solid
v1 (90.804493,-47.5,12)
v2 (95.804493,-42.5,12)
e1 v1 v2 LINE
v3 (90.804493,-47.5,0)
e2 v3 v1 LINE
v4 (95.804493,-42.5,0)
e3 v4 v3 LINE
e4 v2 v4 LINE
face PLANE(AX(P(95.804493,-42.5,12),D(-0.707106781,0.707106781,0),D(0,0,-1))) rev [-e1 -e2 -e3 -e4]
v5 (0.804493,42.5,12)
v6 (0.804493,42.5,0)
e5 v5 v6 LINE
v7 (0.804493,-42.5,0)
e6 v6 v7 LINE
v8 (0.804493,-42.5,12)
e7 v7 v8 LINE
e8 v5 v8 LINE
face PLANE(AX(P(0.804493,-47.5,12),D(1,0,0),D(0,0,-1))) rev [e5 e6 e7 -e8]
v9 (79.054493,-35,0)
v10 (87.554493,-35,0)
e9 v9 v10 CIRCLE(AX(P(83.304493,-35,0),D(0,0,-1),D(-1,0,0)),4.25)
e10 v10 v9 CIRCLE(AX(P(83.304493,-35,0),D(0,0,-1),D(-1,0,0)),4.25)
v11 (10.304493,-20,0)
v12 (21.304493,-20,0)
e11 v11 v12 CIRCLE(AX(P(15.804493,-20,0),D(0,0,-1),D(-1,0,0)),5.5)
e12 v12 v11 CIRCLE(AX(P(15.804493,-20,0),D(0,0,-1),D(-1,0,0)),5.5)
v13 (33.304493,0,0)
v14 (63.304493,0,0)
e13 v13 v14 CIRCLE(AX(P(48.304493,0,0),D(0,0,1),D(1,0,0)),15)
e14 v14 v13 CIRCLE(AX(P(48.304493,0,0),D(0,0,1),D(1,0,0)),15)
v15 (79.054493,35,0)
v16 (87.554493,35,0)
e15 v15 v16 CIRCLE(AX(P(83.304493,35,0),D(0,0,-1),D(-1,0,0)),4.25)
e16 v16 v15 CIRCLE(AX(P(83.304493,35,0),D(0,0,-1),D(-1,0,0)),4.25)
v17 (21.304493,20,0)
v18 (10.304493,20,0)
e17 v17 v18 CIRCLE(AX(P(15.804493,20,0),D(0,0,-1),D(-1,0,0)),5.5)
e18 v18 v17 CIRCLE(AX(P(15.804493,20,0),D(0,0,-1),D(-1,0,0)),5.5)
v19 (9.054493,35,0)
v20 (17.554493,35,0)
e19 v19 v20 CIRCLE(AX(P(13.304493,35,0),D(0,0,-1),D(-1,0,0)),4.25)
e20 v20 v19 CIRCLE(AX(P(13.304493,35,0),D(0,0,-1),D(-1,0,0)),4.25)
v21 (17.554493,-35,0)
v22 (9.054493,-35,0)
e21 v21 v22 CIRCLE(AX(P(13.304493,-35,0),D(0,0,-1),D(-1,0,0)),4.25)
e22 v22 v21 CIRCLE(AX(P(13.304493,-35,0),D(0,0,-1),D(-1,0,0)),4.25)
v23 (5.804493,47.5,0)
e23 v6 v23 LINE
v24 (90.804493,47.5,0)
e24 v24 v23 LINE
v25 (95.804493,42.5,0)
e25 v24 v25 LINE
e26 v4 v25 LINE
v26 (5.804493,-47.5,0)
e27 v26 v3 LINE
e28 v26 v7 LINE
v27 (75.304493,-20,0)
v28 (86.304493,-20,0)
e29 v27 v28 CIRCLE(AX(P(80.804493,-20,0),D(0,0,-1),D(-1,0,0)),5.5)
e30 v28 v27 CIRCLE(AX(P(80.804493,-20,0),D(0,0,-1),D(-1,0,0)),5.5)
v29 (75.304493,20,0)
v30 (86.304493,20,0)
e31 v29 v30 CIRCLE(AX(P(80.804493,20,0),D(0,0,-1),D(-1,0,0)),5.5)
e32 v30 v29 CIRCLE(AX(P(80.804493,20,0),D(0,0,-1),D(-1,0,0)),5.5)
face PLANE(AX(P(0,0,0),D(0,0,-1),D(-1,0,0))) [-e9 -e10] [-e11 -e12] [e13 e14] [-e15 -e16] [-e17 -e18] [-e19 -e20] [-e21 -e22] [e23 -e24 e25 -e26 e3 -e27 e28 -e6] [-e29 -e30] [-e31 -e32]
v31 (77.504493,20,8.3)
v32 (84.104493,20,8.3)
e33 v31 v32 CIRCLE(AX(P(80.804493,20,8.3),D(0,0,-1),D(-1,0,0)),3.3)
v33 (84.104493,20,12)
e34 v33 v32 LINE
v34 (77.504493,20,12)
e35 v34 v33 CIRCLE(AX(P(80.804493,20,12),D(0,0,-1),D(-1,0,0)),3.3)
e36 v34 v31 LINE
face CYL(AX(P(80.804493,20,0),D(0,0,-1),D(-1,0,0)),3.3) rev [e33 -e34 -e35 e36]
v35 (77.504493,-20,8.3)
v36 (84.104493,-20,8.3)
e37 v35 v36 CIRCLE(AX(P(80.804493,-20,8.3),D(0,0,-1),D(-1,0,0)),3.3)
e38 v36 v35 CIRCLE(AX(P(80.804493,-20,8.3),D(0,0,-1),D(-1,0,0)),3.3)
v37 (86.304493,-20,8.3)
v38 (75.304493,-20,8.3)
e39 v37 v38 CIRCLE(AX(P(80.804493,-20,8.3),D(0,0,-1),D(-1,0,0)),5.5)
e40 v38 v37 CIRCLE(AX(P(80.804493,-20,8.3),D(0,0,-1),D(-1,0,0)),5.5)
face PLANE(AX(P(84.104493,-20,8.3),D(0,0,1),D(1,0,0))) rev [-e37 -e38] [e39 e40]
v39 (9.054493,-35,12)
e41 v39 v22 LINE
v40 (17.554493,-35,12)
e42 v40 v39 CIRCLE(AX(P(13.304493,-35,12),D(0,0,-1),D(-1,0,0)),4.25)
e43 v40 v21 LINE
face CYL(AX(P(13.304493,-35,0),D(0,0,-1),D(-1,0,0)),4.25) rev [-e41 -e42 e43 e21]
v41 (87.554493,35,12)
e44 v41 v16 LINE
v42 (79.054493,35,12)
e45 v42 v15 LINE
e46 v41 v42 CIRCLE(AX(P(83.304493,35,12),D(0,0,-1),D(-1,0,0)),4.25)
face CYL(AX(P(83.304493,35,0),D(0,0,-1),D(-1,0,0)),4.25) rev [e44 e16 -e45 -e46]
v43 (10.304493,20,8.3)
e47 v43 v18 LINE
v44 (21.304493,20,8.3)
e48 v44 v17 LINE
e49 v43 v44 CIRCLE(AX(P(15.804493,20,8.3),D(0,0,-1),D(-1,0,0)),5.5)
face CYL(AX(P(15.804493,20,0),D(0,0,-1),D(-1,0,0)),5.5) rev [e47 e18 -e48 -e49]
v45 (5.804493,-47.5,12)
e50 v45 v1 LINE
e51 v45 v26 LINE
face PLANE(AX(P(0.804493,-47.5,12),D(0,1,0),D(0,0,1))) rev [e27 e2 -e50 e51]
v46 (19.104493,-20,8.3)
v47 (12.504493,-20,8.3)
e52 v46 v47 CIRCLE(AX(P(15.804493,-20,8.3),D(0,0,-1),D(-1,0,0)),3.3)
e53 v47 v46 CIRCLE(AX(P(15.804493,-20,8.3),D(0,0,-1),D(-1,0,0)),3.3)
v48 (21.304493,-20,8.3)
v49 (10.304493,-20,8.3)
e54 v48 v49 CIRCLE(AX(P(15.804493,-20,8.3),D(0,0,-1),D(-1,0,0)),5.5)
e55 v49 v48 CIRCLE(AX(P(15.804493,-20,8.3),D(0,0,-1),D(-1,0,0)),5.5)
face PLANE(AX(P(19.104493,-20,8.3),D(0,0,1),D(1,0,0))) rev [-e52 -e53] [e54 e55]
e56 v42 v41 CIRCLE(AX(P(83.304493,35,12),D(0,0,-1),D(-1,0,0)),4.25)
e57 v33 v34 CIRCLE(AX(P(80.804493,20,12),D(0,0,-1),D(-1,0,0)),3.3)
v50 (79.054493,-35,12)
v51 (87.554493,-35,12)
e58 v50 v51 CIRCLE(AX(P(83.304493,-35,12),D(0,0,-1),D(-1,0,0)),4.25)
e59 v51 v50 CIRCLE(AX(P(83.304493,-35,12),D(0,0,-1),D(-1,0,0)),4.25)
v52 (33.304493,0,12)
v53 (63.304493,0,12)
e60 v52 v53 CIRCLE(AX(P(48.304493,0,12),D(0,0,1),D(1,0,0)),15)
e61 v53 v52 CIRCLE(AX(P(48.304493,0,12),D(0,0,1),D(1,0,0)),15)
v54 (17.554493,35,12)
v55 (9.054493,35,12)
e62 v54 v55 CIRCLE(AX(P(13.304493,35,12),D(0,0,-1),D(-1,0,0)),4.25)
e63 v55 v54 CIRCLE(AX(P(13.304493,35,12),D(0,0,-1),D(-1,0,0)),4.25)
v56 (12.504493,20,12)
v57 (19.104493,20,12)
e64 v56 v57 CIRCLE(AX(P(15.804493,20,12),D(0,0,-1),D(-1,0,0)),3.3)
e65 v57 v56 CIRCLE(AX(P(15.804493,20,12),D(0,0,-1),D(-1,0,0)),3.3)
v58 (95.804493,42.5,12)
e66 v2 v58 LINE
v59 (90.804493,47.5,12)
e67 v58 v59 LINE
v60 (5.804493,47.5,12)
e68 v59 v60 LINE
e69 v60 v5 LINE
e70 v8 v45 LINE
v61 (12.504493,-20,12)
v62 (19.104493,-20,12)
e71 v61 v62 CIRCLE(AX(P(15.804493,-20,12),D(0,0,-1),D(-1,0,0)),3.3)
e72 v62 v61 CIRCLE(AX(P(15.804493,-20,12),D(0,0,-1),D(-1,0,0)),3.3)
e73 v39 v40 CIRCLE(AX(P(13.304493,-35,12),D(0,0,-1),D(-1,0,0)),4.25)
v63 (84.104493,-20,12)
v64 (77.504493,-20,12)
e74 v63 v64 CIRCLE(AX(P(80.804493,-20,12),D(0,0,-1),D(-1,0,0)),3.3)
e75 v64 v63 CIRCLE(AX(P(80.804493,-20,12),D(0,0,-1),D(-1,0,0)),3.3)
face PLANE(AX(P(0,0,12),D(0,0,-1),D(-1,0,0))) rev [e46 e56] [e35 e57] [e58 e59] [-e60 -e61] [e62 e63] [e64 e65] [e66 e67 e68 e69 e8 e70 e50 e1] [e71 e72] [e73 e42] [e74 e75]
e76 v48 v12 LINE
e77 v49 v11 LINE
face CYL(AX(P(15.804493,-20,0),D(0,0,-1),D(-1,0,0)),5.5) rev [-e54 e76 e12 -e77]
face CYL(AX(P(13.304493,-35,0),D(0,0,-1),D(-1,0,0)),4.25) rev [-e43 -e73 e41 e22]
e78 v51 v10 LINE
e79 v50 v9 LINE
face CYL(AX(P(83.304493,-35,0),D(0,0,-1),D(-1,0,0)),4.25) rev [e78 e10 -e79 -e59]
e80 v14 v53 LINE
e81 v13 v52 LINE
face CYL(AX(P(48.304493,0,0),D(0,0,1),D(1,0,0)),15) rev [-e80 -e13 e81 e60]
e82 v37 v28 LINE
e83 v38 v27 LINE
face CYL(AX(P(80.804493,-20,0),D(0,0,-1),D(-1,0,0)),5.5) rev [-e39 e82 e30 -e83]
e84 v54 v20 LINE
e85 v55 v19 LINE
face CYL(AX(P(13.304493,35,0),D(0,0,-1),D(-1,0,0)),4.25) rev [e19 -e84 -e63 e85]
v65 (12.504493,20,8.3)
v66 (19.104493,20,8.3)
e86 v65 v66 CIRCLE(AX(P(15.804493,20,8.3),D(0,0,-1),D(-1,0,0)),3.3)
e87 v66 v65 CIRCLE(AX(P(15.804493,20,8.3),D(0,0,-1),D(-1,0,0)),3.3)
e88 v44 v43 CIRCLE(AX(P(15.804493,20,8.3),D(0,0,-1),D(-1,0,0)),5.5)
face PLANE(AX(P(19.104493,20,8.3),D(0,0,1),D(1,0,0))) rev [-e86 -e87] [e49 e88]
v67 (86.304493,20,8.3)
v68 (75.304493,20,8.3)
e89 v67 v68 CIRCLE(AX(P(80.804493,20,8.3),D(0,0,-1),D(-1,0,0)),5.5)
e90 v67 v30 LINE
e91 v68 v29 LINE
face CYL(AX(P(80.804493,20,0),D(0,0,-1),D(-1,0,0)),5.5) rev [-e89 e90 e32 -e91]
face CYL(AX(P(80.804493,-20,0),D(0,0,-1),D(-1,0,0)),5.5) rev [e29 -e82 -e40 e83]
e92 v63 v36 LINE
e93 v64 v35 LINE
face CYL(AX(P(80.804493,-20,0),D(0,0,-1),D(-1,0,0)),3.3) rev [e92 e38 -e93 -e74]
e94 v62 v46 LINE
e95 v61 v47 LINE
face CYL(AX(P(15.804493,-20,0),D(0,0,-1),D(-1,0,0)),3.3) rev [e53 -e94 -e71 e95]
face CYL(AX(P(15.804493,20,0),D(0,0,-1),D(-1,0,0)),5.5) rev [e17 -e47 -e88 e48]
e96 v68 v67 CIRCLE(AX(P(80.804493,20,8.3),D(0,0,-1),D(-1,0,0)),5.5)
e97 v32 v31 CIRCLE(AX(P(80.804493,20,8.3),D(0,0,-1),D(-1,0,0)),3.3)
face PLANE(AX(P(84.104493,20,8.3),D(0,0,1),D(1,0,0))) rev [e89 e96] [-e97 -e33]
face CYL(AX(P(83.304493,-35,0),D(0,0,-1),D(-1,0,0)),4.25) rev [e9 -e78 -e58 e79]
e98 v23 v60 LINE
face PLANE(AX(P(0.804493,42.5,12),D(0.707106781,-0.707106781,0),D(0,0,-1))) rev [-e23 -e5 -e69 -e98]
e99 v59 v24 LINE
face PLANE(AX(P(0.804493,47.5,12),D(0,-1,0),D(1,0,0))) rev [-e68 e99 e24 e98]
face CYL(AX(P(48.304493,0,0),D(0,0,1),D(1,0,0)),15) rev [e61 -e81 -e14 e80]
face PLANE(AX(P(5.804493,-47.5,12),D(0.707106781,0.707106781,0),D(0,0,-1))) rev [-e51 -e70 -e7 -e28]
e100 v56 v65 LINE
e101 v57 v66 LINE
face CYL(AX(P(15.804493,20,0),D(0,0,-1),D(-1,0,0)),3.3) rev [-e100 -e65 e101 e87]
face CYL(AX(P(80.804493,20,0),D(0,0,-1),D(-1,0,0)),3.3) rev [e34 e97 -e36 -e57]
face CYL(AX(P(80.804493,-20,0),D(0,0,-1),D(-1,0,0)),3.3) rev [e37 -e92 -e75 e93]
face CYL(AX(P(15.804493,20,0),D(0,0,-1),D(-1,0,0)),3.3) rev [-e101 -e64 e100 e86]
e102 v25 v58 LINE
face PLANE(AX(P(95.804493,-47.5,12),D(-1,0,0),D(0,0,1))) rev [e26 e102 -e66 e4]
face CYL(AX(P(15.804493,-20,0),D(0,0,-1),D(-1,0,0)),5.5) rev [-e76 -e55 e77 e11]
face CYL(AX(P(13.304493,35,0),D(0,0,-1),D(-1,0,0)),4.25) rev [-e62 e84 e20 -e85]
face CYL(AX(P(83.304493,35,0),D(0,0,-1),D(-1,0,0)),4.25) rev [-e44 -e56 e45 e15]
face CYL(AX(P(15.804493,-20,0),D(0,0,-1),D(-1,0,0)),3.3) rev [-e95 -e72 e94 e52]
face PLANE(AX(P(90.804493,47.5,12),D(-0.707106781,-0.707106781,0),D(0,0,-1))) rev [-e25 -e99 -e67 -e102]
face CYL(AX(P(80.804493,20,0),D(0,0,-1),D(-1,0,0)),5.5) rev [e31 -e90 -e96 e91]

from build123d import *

# Parameters (mm, degrees)
SKETCH_1_W                = 95
SKETCH_1_H                = 95
EXTRUDE_1_DEPTH           = 12
SKETCH_2_R                = 15
CUT_EXTRUDE_1_DEPTH       = 108.604604424
HOLE_WIZARD_1_D           = 6.6
HOLE_WIZARD_1_CBORE_D     = 11
HOLE_WIZARD_1_CBORE_DEPTH = 8.3
HOLE_WIZARD_M10_2_D       = 8.5
CHAMFER_1_SIZE            = 5


with BuildPart() as part:
    # 草图1 → 凸台-拉伸1 (new body)
    with BuildSketch(Plane.XY):
        with Locations((48.304493075, 0)):
            Rectangle(SKETCH_1_W, SKETCH_1_H)
    extrude(amount=EXTRUDE_1_DEPTH)

    # 草图2 → 切除-拉伸1 (cut, through all)
    with BuildSketch(Plane.XY.offset(12)):
        with Locations((48.304493075, 0)):
            Circle(SKETCH_2_R)
    extrude(amount=-CUT_EXTRUDE_1_DEPTH, mode=Mode.SUBTRACT)

    # 打孔尺寸(%根据)内六角圆柱头螺钉的类型1 (through all)
    with Locations(Plane(origin=(80.804493075, 20, 0), x_dir=(-1, 0, 0), z_dir=(0, 0, -1))):
        with Locations((0, 0), (65, 0), (65, -40), (0, -40)):
            CounterBoreHole(HOLE_WIZARD_1_D / 2, HOLE_WIZARD_1_CBORE_D / 2, HOLE_WIZARD_1_CBORE_DEPTH)

    # M10 螺纹孔2 (through all)
    with Locations(Plane(origin=(83.304493075, 35, 0), x_dir=(-1, 0, 0), z_dir=(0, 0, -1))):
        with Locations((0, 0), (70, 0), (70, -70), (0, -70)):
            Hole(HOLE_WIZARD_M10_2_D / 2)

    # 倒角1
    chamfer_1_edges = [part.edges().sort_by_distance(p)[0] for p in [
        (0.804493075, 47.5, 6),
        (95.804493075, 47.5, 6),
        (95.804493075, -47.5, 6),
        (0.804493075, -47.5, 6),
    ]]
    chamfer(chamfer_1_edges, length=CHAMFER_1_SIZE)


solid = part.part
